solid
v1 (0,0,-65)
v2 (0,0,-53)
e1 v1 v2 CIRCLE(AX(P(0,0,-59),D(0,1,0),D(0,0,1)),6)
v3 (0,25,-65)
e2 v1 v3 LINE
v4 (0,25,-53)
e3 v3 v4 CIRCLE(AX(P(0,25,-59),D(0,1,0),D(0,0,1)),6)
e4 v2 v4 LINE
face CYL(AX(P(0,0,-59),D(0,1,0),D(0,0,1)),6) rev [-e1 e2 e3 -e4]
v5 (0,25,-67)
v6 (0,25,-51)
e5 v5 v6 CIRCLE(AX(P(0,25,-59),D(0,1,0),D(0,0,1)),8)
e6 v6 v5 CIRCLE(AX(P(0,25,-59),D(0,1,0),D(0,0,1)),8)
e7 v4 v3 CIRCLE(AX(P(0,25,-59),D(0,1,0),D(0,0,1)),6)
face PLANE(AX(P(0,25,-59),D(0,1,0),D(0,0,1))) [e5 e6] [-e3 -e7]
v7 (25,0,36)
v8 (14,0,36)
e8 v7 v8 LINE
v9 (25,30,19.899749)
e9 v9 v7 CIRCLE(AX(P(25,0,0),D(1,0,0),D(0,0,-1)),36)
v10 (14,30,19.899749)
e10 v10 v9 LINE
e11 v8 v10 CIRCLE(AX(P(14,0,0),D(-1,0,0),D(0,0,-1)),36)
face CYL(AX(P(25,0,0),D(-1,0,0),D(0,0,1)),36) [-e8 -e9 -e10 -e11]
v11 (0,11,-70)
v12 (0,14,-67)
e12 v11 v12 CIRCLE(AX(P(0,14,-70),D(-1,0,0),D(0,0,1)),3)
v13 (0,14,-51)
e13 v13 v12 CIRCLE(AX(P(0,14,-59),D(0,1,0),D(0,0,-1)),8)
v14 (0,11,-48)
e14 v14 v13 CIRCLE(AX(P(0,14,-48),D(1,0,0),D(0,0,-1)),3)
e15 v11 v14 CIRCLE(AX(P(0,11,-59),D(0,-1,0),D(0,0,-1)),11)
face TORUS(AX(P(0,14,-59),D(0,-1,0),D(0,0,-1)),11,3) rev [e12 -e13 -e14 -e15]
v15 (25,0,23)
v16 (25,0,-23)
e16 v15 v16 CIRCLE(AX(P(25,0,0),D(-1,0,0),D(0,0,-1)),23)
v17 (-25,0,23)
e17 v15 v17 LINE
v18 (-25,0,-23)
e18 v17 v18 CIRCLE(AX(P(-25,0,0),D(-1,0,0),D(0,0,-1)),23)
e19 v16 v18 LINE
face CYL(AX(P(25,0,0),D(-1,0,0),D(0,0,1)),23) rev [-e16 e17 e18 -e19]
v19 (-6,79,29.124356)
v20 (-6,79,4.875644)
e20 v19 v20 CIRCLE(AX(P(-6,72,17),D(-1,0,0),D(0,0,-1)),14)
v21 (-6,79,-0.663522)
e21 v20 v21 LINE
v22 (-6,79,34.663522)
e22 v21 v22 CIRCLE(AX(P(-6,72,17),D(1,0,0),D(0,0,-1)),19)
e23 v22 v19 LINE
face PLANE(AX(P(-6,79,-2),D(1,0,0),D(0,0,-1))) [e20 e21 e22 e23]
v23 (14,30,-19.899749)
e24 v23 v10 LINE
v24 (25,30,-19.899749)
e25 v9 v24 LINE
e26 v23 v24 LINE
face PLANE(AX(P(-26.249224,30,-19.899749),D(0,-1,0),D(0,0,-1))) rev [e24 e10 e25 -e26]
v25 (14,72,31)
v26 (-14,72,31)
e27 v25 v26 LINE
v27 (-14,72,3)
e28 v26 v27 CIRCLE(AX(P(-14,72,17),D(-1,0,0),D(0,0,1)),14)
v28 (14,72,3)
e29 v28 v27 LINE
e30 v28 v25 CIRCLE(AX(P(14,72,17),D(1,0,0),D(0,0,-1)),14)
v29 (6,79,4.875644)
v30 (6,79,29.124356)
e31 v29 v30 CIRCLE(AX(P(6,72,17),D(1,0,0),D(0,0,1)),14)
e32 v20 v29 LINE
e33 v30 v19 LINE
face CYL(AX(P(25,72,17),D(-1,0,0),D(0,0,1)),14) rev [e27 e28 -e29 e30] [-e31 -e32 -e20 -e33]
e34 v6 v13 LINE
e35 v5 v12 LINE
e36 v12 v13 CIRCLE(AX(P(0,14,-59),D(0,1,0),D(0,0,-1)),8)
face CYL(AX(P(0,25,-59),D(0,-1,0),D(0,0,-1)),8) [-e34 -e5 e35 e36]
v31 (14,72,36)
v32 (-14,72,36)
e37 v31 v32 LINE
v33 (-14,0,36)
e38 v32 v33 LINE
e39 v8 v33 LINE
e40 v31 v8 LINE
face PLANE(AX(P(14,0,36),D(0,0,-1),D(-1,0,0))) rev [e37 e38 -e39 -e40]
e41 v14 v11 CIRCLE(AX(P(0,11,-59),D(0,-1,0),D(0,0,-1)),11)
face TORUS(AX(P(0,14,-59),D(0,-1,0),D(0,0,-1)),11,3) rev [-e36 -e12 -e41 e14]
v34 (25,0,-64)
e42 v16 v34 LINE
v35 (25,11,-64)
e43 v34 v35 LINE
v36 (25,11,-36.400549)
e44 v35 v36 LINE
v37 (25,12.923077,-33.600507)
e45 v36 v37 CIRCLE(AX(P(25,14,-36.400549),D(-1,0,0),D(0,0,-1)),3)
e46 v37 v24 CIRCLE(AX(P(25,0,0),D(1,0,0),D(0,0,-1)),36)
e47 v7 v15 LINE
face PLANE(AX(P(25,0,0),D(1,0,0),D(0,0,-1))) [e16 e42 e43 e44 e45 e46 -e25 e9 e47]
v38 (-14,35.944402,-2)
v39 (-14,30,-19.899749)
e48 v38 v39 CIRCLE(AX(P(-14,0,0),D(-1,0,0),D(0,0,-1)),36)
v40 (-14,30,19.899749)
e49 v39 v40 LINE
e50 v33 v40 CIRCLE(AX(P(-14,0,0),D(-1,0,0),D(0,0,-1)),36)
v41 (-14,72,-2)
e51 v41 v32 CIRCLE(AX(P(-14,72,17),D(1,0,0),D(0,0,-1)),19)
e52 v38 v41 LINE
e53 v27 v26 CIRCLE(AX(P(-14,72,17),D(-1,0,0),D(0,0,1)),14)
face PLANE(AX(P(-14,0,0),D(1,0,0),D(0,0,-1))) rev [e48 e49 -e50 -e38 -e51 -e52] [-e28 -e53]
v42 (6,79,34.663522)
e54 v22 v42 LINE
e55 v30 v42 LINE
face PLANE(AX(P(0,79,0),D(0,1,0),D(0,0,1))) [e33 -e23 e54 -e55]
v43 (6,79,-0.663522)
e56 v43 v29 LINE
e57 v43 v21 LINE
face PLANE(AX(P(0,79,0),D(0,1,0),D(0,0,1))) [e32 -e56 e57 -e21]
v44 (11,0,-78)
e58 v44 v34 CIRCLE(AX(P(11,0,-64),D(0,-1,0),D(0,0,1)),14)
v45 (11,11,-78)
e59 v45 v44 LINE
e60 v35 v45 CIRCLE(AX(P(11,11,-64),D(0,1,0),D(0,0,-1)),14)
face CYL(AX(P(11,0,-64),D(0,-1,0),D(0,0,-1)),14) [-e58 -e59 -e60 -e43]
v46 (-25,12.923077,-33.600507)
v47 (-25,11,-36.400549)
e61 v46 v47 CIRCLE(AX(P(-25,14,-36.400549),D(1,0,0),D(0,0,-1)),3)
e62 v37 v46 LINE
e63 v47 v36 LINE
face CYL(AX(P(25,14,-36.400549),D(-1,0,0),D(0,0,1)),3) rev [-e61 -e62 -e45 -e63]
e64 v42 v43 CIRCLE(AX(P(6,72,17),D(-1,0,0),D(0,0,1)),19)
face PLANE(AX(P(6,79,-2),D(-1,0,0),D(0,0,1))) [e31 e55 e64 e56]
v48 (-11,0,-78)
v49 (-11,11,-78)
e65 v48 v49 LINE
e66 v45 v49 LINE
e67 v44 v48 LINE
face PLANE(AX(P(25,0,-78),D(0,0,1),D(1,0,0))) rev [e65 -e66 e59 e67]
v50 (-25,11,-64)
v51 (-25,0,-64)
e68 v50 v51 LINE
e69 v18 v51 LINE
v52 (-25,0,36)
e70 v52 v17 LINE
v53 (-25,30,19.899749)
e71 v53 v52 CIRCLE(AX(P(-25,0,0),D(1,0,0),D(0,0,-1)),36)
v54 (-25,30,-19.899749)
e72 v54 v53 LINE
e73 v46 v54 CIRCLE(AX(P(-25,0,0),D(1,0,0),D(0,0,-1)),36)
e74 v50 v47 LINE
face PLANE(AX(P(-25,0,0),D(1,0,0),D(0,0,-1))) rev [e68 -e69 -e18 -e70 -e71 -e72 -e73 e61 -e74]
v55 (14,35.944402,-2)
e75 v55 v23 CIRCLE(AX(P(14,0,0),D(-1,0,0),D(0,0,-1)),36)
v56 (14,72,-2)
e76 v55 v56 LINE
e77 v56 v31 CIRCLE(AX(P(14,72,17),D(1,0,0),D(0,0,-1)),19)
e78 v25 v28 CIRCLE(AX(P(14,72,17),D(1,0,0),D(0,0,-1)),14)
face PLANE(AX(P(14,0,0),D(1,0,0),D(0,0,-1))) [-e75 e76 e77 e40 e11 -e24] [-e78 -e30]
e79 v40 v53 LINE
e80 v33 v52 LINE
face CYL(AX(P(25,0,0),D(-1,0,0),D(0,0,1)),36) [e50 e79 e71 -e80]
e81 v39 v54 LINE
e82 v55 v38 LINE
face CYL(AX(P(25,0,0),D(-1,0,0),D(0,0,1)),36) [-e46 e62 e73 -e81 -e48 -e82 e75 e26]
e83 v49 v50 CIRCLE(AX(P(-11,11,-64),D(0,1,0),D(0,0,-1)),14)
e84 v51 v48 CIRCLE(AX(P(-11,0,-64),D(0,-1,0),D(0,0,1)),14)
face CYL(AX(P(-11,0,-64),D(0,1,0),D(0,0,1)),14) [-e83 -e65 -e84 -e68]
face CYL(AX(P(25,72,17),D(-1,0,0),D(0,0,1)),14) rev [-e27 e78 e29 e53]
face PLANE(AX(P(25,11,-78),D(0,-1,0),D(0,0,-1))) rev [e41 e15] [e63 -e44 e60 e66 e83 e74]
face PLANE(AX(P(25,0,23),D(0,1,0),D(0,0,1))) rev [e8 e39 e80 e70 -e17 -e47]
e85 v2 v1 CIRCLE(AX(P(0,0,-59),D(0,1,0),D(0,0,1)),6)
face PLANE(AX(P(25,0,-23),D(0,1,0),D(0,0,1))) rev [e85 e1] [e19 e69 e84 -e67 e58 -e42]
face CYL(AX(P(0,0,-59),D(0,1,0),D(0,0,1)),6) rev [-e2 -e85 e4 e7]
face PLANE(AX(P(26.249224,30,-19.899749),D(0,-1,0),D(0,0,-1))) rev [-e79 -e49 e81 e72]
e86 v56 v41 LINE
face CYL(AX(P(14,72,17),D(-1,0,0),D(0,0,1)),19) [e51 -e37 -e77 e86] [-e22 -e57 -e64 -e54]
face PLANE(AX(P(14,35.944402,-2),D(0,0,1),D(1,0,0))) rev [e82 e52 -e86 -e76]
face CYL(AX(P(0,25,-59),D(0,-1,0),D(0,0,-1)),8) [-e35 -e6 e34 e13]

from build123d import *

# Parameters (mm, degrees)
BASE_SADDLE_DEPTH          = 25
BASE_CORNER_FILLET_R14_R   = 14
PIN_BOSS_SKETCH_R          = 8
PIVOT_PIN_BOSS_16_DEPTH    = 14
PIN_BOSS_BORE_SKETCH_R     = 6
PIN_BOSS_BORE_12_DEPTH     = 86.638776264
PIN_BOSS_ROOT_FILLET_R3_R  = 3
CLEVIS_UPRIGHT_DEPTH       = 14
EYE_BOSS_SKETCH_R          = 19
EYE_BOSS_DEPTH             = 14
EYE_BORE_SKETCH_R          = 14
EYE_BORE_28_DEPTH          = 127.039676293
SADDLE_START               = -11
SADDLE_CLEARANCE_CUT_DEPTH = 11
SADDLE_RELIEF_CUT_DEPTH    = 11
CLEVIS_SLOT_SKETCH_W       = 12
CLEVIS_SLOT_SKETCH_H       = 38
CLEVIS_SLOT_12_DEPTH       = 12


with BuildPart() as part:
    # Base Saddle Profile Sketch → Base Saddle (new, symmetric)
    with BuildSketch(Plane(origin=(0, 0, 0), x_dir=(0, 0, -1), z_dir=(1, 0, 0))):
        with BuildLine():
            Line((23, 0), (78, 0))
            Line((78, 0), (78, 11))
            Line((78, 11), (34.278273002, 11))
            ThreePointArc((34.278273002, 11), (-5.566963801, 35.566963801), (-36, 0))
            Line((-36, 0), (-23, 0))
            ThreePointArc((-23, 0), (0, 23), (23, 0))
        make_face()
    extrude(amount=BASE_SADDLE_DEPTH, both=True)

    # Base Corner Fillet R14
    base_corner_fillet_r14_edges = [part.edges().sort_by_distance(p)[0] for p in [
        (25, 5.5, -78),
        (-25, 5.5, -78),
    ]]
    fillet(base_corner_fillet_r14_edges, radius=BASE_CORNER_FILLET_R14_R)

    # Pin Boss Sketch → Pivot Pin Boss Ø16 (add)
    with BuildSketch(Plane(origin=(0, 11, 0), x_dir=(1, 0, 0), z_dir=(0, 1, 0))):
        with Locations(Location((0, 59, 0), (0, 0, 90))):
            Circle(PIN_BOSS_SKETCH_R)
    extrude(amount=PIVOT_PIN_BOSS_16_DEPTH)

    # Pin Boss Bore Sketch → Pin Boss Bore Ø12 (cut, through all)
    with BuildSketch(Plane(origin=(0, 25, 0), x_dir=(1, 0, 0), z_dir=(0, 1, 0))):
        with Locations(Location((0, 59, 0), (0, 0, 270))):
            Circle(PIN_BOSS_BORE_SKETCH_R)
    extrude(amount=-PIN_BOSS_BORE_12_DEPTH, mode=Mode.SUBTRACT)

    # Pin Boss Root Fillet R3
    pin_boss_root_fillet_r3_edges = [part.edges().sort_by_distance(p)[0] for p in [
        (0, 11, -34.278273002),
        (0, 11, -51),
    ]]
    fillet(pin_boss_root_fillet_r3_edges, radius=PIN_BOSS_ROOT_FILLET_R3_R)

    # Clevis Upright Sketch → Clevis Upright (add, symmetric)
    with BuildSketch(Plane(origin=(0, 0, 0), x_dir=(0, 0, -1), z_dir=(1, 0, 0))):
        with BuildLine():
            Line((-36, 0), (-36, 72))
            Line((-36, 72), (2, 72))
            Line((2, 72), (2, 35.944401511))
            ThreePointArc((2, 35.944401511), (-24.738633754, 26.153393661), (-36, 0))
        make_face()
    extrude(amount=CLEVIS_UPRIGHT_DEPTH, both=True)

    # Eye Boss Sketch → Eye Boss (add, symmetric)
    with BuildSketch(Plane(origin=(0, 0, 0), x_dir=(0, 0, -1), z_dir=(1, 0, 0))):
        with Locations((-17, 72)):
            Circle(EYE_BOSS_SKETCH_R)
    extrude(amount=EYE_BOSS_DEPTH, both=True)

    # Eye Bore Sketch → Eye Bore Ø28 (cut, through all)
    with BuildSketch(Plane.ZY.offset(14)):
        with Locations((17, 72)):
            Circle(EYE_BORE_SKETCH_R)
    extrude(amount=-EYE_BORE_28_DEPTH, mode=Mode.SUBTRACT)

    # Saddle Clearance Sketch → Saddle Clearance Cut (cut)
    with BuildSketch(Plane.ZY.offset(25).offset(SADDLE_START)):
        with BuildLine():
            Line((-19.899748742, 30), (19.899748742, 30))
            ThreePointArc((19.899748742, 30), (0, 36), (-19.899748742, 30))
        make_face()
    extrude(amount=SADDLE_CLEARANCE_CUT_DEPTH, mode=Mode.SUBTRACT)

    # Saddle Relief Sketch → Saddle Relief Cut (cut)
    with BuildSketch(Plane(origin=(25, 0, 0), x_dir=(0, 0, -1), z_dir=(1, 0, 0))):
        with BuildLine():
            Line((19.899748742, 30), (-19.899748742, 30))
            ThreePointArc((-19.899748742, 30), (0, 36), (19.899748742, 30))
        make_face()
    extrude(amount=-SADDLE_RELIEF_CUT_DEPTH, mode=Mode.SUBTRACT)

    # Clevis Slot Sketch → Clevis Slot 12 (cut)
    with BuildSketch(Plane(origin=(0, 91, 0), x_dir=(-1, 0, 0), z_dir=(0, -1, 0))):
        with Locations((0, -17)):
            Rectangle(CLEVIS_SLOT_SKETCH_W, CLEVIS_SLOT_SKETCH_H)
    extrude(amount=CLEVIS_SLOT_12_DEPTH, mode=Mode.SUBTRACT)


solid = part.part
